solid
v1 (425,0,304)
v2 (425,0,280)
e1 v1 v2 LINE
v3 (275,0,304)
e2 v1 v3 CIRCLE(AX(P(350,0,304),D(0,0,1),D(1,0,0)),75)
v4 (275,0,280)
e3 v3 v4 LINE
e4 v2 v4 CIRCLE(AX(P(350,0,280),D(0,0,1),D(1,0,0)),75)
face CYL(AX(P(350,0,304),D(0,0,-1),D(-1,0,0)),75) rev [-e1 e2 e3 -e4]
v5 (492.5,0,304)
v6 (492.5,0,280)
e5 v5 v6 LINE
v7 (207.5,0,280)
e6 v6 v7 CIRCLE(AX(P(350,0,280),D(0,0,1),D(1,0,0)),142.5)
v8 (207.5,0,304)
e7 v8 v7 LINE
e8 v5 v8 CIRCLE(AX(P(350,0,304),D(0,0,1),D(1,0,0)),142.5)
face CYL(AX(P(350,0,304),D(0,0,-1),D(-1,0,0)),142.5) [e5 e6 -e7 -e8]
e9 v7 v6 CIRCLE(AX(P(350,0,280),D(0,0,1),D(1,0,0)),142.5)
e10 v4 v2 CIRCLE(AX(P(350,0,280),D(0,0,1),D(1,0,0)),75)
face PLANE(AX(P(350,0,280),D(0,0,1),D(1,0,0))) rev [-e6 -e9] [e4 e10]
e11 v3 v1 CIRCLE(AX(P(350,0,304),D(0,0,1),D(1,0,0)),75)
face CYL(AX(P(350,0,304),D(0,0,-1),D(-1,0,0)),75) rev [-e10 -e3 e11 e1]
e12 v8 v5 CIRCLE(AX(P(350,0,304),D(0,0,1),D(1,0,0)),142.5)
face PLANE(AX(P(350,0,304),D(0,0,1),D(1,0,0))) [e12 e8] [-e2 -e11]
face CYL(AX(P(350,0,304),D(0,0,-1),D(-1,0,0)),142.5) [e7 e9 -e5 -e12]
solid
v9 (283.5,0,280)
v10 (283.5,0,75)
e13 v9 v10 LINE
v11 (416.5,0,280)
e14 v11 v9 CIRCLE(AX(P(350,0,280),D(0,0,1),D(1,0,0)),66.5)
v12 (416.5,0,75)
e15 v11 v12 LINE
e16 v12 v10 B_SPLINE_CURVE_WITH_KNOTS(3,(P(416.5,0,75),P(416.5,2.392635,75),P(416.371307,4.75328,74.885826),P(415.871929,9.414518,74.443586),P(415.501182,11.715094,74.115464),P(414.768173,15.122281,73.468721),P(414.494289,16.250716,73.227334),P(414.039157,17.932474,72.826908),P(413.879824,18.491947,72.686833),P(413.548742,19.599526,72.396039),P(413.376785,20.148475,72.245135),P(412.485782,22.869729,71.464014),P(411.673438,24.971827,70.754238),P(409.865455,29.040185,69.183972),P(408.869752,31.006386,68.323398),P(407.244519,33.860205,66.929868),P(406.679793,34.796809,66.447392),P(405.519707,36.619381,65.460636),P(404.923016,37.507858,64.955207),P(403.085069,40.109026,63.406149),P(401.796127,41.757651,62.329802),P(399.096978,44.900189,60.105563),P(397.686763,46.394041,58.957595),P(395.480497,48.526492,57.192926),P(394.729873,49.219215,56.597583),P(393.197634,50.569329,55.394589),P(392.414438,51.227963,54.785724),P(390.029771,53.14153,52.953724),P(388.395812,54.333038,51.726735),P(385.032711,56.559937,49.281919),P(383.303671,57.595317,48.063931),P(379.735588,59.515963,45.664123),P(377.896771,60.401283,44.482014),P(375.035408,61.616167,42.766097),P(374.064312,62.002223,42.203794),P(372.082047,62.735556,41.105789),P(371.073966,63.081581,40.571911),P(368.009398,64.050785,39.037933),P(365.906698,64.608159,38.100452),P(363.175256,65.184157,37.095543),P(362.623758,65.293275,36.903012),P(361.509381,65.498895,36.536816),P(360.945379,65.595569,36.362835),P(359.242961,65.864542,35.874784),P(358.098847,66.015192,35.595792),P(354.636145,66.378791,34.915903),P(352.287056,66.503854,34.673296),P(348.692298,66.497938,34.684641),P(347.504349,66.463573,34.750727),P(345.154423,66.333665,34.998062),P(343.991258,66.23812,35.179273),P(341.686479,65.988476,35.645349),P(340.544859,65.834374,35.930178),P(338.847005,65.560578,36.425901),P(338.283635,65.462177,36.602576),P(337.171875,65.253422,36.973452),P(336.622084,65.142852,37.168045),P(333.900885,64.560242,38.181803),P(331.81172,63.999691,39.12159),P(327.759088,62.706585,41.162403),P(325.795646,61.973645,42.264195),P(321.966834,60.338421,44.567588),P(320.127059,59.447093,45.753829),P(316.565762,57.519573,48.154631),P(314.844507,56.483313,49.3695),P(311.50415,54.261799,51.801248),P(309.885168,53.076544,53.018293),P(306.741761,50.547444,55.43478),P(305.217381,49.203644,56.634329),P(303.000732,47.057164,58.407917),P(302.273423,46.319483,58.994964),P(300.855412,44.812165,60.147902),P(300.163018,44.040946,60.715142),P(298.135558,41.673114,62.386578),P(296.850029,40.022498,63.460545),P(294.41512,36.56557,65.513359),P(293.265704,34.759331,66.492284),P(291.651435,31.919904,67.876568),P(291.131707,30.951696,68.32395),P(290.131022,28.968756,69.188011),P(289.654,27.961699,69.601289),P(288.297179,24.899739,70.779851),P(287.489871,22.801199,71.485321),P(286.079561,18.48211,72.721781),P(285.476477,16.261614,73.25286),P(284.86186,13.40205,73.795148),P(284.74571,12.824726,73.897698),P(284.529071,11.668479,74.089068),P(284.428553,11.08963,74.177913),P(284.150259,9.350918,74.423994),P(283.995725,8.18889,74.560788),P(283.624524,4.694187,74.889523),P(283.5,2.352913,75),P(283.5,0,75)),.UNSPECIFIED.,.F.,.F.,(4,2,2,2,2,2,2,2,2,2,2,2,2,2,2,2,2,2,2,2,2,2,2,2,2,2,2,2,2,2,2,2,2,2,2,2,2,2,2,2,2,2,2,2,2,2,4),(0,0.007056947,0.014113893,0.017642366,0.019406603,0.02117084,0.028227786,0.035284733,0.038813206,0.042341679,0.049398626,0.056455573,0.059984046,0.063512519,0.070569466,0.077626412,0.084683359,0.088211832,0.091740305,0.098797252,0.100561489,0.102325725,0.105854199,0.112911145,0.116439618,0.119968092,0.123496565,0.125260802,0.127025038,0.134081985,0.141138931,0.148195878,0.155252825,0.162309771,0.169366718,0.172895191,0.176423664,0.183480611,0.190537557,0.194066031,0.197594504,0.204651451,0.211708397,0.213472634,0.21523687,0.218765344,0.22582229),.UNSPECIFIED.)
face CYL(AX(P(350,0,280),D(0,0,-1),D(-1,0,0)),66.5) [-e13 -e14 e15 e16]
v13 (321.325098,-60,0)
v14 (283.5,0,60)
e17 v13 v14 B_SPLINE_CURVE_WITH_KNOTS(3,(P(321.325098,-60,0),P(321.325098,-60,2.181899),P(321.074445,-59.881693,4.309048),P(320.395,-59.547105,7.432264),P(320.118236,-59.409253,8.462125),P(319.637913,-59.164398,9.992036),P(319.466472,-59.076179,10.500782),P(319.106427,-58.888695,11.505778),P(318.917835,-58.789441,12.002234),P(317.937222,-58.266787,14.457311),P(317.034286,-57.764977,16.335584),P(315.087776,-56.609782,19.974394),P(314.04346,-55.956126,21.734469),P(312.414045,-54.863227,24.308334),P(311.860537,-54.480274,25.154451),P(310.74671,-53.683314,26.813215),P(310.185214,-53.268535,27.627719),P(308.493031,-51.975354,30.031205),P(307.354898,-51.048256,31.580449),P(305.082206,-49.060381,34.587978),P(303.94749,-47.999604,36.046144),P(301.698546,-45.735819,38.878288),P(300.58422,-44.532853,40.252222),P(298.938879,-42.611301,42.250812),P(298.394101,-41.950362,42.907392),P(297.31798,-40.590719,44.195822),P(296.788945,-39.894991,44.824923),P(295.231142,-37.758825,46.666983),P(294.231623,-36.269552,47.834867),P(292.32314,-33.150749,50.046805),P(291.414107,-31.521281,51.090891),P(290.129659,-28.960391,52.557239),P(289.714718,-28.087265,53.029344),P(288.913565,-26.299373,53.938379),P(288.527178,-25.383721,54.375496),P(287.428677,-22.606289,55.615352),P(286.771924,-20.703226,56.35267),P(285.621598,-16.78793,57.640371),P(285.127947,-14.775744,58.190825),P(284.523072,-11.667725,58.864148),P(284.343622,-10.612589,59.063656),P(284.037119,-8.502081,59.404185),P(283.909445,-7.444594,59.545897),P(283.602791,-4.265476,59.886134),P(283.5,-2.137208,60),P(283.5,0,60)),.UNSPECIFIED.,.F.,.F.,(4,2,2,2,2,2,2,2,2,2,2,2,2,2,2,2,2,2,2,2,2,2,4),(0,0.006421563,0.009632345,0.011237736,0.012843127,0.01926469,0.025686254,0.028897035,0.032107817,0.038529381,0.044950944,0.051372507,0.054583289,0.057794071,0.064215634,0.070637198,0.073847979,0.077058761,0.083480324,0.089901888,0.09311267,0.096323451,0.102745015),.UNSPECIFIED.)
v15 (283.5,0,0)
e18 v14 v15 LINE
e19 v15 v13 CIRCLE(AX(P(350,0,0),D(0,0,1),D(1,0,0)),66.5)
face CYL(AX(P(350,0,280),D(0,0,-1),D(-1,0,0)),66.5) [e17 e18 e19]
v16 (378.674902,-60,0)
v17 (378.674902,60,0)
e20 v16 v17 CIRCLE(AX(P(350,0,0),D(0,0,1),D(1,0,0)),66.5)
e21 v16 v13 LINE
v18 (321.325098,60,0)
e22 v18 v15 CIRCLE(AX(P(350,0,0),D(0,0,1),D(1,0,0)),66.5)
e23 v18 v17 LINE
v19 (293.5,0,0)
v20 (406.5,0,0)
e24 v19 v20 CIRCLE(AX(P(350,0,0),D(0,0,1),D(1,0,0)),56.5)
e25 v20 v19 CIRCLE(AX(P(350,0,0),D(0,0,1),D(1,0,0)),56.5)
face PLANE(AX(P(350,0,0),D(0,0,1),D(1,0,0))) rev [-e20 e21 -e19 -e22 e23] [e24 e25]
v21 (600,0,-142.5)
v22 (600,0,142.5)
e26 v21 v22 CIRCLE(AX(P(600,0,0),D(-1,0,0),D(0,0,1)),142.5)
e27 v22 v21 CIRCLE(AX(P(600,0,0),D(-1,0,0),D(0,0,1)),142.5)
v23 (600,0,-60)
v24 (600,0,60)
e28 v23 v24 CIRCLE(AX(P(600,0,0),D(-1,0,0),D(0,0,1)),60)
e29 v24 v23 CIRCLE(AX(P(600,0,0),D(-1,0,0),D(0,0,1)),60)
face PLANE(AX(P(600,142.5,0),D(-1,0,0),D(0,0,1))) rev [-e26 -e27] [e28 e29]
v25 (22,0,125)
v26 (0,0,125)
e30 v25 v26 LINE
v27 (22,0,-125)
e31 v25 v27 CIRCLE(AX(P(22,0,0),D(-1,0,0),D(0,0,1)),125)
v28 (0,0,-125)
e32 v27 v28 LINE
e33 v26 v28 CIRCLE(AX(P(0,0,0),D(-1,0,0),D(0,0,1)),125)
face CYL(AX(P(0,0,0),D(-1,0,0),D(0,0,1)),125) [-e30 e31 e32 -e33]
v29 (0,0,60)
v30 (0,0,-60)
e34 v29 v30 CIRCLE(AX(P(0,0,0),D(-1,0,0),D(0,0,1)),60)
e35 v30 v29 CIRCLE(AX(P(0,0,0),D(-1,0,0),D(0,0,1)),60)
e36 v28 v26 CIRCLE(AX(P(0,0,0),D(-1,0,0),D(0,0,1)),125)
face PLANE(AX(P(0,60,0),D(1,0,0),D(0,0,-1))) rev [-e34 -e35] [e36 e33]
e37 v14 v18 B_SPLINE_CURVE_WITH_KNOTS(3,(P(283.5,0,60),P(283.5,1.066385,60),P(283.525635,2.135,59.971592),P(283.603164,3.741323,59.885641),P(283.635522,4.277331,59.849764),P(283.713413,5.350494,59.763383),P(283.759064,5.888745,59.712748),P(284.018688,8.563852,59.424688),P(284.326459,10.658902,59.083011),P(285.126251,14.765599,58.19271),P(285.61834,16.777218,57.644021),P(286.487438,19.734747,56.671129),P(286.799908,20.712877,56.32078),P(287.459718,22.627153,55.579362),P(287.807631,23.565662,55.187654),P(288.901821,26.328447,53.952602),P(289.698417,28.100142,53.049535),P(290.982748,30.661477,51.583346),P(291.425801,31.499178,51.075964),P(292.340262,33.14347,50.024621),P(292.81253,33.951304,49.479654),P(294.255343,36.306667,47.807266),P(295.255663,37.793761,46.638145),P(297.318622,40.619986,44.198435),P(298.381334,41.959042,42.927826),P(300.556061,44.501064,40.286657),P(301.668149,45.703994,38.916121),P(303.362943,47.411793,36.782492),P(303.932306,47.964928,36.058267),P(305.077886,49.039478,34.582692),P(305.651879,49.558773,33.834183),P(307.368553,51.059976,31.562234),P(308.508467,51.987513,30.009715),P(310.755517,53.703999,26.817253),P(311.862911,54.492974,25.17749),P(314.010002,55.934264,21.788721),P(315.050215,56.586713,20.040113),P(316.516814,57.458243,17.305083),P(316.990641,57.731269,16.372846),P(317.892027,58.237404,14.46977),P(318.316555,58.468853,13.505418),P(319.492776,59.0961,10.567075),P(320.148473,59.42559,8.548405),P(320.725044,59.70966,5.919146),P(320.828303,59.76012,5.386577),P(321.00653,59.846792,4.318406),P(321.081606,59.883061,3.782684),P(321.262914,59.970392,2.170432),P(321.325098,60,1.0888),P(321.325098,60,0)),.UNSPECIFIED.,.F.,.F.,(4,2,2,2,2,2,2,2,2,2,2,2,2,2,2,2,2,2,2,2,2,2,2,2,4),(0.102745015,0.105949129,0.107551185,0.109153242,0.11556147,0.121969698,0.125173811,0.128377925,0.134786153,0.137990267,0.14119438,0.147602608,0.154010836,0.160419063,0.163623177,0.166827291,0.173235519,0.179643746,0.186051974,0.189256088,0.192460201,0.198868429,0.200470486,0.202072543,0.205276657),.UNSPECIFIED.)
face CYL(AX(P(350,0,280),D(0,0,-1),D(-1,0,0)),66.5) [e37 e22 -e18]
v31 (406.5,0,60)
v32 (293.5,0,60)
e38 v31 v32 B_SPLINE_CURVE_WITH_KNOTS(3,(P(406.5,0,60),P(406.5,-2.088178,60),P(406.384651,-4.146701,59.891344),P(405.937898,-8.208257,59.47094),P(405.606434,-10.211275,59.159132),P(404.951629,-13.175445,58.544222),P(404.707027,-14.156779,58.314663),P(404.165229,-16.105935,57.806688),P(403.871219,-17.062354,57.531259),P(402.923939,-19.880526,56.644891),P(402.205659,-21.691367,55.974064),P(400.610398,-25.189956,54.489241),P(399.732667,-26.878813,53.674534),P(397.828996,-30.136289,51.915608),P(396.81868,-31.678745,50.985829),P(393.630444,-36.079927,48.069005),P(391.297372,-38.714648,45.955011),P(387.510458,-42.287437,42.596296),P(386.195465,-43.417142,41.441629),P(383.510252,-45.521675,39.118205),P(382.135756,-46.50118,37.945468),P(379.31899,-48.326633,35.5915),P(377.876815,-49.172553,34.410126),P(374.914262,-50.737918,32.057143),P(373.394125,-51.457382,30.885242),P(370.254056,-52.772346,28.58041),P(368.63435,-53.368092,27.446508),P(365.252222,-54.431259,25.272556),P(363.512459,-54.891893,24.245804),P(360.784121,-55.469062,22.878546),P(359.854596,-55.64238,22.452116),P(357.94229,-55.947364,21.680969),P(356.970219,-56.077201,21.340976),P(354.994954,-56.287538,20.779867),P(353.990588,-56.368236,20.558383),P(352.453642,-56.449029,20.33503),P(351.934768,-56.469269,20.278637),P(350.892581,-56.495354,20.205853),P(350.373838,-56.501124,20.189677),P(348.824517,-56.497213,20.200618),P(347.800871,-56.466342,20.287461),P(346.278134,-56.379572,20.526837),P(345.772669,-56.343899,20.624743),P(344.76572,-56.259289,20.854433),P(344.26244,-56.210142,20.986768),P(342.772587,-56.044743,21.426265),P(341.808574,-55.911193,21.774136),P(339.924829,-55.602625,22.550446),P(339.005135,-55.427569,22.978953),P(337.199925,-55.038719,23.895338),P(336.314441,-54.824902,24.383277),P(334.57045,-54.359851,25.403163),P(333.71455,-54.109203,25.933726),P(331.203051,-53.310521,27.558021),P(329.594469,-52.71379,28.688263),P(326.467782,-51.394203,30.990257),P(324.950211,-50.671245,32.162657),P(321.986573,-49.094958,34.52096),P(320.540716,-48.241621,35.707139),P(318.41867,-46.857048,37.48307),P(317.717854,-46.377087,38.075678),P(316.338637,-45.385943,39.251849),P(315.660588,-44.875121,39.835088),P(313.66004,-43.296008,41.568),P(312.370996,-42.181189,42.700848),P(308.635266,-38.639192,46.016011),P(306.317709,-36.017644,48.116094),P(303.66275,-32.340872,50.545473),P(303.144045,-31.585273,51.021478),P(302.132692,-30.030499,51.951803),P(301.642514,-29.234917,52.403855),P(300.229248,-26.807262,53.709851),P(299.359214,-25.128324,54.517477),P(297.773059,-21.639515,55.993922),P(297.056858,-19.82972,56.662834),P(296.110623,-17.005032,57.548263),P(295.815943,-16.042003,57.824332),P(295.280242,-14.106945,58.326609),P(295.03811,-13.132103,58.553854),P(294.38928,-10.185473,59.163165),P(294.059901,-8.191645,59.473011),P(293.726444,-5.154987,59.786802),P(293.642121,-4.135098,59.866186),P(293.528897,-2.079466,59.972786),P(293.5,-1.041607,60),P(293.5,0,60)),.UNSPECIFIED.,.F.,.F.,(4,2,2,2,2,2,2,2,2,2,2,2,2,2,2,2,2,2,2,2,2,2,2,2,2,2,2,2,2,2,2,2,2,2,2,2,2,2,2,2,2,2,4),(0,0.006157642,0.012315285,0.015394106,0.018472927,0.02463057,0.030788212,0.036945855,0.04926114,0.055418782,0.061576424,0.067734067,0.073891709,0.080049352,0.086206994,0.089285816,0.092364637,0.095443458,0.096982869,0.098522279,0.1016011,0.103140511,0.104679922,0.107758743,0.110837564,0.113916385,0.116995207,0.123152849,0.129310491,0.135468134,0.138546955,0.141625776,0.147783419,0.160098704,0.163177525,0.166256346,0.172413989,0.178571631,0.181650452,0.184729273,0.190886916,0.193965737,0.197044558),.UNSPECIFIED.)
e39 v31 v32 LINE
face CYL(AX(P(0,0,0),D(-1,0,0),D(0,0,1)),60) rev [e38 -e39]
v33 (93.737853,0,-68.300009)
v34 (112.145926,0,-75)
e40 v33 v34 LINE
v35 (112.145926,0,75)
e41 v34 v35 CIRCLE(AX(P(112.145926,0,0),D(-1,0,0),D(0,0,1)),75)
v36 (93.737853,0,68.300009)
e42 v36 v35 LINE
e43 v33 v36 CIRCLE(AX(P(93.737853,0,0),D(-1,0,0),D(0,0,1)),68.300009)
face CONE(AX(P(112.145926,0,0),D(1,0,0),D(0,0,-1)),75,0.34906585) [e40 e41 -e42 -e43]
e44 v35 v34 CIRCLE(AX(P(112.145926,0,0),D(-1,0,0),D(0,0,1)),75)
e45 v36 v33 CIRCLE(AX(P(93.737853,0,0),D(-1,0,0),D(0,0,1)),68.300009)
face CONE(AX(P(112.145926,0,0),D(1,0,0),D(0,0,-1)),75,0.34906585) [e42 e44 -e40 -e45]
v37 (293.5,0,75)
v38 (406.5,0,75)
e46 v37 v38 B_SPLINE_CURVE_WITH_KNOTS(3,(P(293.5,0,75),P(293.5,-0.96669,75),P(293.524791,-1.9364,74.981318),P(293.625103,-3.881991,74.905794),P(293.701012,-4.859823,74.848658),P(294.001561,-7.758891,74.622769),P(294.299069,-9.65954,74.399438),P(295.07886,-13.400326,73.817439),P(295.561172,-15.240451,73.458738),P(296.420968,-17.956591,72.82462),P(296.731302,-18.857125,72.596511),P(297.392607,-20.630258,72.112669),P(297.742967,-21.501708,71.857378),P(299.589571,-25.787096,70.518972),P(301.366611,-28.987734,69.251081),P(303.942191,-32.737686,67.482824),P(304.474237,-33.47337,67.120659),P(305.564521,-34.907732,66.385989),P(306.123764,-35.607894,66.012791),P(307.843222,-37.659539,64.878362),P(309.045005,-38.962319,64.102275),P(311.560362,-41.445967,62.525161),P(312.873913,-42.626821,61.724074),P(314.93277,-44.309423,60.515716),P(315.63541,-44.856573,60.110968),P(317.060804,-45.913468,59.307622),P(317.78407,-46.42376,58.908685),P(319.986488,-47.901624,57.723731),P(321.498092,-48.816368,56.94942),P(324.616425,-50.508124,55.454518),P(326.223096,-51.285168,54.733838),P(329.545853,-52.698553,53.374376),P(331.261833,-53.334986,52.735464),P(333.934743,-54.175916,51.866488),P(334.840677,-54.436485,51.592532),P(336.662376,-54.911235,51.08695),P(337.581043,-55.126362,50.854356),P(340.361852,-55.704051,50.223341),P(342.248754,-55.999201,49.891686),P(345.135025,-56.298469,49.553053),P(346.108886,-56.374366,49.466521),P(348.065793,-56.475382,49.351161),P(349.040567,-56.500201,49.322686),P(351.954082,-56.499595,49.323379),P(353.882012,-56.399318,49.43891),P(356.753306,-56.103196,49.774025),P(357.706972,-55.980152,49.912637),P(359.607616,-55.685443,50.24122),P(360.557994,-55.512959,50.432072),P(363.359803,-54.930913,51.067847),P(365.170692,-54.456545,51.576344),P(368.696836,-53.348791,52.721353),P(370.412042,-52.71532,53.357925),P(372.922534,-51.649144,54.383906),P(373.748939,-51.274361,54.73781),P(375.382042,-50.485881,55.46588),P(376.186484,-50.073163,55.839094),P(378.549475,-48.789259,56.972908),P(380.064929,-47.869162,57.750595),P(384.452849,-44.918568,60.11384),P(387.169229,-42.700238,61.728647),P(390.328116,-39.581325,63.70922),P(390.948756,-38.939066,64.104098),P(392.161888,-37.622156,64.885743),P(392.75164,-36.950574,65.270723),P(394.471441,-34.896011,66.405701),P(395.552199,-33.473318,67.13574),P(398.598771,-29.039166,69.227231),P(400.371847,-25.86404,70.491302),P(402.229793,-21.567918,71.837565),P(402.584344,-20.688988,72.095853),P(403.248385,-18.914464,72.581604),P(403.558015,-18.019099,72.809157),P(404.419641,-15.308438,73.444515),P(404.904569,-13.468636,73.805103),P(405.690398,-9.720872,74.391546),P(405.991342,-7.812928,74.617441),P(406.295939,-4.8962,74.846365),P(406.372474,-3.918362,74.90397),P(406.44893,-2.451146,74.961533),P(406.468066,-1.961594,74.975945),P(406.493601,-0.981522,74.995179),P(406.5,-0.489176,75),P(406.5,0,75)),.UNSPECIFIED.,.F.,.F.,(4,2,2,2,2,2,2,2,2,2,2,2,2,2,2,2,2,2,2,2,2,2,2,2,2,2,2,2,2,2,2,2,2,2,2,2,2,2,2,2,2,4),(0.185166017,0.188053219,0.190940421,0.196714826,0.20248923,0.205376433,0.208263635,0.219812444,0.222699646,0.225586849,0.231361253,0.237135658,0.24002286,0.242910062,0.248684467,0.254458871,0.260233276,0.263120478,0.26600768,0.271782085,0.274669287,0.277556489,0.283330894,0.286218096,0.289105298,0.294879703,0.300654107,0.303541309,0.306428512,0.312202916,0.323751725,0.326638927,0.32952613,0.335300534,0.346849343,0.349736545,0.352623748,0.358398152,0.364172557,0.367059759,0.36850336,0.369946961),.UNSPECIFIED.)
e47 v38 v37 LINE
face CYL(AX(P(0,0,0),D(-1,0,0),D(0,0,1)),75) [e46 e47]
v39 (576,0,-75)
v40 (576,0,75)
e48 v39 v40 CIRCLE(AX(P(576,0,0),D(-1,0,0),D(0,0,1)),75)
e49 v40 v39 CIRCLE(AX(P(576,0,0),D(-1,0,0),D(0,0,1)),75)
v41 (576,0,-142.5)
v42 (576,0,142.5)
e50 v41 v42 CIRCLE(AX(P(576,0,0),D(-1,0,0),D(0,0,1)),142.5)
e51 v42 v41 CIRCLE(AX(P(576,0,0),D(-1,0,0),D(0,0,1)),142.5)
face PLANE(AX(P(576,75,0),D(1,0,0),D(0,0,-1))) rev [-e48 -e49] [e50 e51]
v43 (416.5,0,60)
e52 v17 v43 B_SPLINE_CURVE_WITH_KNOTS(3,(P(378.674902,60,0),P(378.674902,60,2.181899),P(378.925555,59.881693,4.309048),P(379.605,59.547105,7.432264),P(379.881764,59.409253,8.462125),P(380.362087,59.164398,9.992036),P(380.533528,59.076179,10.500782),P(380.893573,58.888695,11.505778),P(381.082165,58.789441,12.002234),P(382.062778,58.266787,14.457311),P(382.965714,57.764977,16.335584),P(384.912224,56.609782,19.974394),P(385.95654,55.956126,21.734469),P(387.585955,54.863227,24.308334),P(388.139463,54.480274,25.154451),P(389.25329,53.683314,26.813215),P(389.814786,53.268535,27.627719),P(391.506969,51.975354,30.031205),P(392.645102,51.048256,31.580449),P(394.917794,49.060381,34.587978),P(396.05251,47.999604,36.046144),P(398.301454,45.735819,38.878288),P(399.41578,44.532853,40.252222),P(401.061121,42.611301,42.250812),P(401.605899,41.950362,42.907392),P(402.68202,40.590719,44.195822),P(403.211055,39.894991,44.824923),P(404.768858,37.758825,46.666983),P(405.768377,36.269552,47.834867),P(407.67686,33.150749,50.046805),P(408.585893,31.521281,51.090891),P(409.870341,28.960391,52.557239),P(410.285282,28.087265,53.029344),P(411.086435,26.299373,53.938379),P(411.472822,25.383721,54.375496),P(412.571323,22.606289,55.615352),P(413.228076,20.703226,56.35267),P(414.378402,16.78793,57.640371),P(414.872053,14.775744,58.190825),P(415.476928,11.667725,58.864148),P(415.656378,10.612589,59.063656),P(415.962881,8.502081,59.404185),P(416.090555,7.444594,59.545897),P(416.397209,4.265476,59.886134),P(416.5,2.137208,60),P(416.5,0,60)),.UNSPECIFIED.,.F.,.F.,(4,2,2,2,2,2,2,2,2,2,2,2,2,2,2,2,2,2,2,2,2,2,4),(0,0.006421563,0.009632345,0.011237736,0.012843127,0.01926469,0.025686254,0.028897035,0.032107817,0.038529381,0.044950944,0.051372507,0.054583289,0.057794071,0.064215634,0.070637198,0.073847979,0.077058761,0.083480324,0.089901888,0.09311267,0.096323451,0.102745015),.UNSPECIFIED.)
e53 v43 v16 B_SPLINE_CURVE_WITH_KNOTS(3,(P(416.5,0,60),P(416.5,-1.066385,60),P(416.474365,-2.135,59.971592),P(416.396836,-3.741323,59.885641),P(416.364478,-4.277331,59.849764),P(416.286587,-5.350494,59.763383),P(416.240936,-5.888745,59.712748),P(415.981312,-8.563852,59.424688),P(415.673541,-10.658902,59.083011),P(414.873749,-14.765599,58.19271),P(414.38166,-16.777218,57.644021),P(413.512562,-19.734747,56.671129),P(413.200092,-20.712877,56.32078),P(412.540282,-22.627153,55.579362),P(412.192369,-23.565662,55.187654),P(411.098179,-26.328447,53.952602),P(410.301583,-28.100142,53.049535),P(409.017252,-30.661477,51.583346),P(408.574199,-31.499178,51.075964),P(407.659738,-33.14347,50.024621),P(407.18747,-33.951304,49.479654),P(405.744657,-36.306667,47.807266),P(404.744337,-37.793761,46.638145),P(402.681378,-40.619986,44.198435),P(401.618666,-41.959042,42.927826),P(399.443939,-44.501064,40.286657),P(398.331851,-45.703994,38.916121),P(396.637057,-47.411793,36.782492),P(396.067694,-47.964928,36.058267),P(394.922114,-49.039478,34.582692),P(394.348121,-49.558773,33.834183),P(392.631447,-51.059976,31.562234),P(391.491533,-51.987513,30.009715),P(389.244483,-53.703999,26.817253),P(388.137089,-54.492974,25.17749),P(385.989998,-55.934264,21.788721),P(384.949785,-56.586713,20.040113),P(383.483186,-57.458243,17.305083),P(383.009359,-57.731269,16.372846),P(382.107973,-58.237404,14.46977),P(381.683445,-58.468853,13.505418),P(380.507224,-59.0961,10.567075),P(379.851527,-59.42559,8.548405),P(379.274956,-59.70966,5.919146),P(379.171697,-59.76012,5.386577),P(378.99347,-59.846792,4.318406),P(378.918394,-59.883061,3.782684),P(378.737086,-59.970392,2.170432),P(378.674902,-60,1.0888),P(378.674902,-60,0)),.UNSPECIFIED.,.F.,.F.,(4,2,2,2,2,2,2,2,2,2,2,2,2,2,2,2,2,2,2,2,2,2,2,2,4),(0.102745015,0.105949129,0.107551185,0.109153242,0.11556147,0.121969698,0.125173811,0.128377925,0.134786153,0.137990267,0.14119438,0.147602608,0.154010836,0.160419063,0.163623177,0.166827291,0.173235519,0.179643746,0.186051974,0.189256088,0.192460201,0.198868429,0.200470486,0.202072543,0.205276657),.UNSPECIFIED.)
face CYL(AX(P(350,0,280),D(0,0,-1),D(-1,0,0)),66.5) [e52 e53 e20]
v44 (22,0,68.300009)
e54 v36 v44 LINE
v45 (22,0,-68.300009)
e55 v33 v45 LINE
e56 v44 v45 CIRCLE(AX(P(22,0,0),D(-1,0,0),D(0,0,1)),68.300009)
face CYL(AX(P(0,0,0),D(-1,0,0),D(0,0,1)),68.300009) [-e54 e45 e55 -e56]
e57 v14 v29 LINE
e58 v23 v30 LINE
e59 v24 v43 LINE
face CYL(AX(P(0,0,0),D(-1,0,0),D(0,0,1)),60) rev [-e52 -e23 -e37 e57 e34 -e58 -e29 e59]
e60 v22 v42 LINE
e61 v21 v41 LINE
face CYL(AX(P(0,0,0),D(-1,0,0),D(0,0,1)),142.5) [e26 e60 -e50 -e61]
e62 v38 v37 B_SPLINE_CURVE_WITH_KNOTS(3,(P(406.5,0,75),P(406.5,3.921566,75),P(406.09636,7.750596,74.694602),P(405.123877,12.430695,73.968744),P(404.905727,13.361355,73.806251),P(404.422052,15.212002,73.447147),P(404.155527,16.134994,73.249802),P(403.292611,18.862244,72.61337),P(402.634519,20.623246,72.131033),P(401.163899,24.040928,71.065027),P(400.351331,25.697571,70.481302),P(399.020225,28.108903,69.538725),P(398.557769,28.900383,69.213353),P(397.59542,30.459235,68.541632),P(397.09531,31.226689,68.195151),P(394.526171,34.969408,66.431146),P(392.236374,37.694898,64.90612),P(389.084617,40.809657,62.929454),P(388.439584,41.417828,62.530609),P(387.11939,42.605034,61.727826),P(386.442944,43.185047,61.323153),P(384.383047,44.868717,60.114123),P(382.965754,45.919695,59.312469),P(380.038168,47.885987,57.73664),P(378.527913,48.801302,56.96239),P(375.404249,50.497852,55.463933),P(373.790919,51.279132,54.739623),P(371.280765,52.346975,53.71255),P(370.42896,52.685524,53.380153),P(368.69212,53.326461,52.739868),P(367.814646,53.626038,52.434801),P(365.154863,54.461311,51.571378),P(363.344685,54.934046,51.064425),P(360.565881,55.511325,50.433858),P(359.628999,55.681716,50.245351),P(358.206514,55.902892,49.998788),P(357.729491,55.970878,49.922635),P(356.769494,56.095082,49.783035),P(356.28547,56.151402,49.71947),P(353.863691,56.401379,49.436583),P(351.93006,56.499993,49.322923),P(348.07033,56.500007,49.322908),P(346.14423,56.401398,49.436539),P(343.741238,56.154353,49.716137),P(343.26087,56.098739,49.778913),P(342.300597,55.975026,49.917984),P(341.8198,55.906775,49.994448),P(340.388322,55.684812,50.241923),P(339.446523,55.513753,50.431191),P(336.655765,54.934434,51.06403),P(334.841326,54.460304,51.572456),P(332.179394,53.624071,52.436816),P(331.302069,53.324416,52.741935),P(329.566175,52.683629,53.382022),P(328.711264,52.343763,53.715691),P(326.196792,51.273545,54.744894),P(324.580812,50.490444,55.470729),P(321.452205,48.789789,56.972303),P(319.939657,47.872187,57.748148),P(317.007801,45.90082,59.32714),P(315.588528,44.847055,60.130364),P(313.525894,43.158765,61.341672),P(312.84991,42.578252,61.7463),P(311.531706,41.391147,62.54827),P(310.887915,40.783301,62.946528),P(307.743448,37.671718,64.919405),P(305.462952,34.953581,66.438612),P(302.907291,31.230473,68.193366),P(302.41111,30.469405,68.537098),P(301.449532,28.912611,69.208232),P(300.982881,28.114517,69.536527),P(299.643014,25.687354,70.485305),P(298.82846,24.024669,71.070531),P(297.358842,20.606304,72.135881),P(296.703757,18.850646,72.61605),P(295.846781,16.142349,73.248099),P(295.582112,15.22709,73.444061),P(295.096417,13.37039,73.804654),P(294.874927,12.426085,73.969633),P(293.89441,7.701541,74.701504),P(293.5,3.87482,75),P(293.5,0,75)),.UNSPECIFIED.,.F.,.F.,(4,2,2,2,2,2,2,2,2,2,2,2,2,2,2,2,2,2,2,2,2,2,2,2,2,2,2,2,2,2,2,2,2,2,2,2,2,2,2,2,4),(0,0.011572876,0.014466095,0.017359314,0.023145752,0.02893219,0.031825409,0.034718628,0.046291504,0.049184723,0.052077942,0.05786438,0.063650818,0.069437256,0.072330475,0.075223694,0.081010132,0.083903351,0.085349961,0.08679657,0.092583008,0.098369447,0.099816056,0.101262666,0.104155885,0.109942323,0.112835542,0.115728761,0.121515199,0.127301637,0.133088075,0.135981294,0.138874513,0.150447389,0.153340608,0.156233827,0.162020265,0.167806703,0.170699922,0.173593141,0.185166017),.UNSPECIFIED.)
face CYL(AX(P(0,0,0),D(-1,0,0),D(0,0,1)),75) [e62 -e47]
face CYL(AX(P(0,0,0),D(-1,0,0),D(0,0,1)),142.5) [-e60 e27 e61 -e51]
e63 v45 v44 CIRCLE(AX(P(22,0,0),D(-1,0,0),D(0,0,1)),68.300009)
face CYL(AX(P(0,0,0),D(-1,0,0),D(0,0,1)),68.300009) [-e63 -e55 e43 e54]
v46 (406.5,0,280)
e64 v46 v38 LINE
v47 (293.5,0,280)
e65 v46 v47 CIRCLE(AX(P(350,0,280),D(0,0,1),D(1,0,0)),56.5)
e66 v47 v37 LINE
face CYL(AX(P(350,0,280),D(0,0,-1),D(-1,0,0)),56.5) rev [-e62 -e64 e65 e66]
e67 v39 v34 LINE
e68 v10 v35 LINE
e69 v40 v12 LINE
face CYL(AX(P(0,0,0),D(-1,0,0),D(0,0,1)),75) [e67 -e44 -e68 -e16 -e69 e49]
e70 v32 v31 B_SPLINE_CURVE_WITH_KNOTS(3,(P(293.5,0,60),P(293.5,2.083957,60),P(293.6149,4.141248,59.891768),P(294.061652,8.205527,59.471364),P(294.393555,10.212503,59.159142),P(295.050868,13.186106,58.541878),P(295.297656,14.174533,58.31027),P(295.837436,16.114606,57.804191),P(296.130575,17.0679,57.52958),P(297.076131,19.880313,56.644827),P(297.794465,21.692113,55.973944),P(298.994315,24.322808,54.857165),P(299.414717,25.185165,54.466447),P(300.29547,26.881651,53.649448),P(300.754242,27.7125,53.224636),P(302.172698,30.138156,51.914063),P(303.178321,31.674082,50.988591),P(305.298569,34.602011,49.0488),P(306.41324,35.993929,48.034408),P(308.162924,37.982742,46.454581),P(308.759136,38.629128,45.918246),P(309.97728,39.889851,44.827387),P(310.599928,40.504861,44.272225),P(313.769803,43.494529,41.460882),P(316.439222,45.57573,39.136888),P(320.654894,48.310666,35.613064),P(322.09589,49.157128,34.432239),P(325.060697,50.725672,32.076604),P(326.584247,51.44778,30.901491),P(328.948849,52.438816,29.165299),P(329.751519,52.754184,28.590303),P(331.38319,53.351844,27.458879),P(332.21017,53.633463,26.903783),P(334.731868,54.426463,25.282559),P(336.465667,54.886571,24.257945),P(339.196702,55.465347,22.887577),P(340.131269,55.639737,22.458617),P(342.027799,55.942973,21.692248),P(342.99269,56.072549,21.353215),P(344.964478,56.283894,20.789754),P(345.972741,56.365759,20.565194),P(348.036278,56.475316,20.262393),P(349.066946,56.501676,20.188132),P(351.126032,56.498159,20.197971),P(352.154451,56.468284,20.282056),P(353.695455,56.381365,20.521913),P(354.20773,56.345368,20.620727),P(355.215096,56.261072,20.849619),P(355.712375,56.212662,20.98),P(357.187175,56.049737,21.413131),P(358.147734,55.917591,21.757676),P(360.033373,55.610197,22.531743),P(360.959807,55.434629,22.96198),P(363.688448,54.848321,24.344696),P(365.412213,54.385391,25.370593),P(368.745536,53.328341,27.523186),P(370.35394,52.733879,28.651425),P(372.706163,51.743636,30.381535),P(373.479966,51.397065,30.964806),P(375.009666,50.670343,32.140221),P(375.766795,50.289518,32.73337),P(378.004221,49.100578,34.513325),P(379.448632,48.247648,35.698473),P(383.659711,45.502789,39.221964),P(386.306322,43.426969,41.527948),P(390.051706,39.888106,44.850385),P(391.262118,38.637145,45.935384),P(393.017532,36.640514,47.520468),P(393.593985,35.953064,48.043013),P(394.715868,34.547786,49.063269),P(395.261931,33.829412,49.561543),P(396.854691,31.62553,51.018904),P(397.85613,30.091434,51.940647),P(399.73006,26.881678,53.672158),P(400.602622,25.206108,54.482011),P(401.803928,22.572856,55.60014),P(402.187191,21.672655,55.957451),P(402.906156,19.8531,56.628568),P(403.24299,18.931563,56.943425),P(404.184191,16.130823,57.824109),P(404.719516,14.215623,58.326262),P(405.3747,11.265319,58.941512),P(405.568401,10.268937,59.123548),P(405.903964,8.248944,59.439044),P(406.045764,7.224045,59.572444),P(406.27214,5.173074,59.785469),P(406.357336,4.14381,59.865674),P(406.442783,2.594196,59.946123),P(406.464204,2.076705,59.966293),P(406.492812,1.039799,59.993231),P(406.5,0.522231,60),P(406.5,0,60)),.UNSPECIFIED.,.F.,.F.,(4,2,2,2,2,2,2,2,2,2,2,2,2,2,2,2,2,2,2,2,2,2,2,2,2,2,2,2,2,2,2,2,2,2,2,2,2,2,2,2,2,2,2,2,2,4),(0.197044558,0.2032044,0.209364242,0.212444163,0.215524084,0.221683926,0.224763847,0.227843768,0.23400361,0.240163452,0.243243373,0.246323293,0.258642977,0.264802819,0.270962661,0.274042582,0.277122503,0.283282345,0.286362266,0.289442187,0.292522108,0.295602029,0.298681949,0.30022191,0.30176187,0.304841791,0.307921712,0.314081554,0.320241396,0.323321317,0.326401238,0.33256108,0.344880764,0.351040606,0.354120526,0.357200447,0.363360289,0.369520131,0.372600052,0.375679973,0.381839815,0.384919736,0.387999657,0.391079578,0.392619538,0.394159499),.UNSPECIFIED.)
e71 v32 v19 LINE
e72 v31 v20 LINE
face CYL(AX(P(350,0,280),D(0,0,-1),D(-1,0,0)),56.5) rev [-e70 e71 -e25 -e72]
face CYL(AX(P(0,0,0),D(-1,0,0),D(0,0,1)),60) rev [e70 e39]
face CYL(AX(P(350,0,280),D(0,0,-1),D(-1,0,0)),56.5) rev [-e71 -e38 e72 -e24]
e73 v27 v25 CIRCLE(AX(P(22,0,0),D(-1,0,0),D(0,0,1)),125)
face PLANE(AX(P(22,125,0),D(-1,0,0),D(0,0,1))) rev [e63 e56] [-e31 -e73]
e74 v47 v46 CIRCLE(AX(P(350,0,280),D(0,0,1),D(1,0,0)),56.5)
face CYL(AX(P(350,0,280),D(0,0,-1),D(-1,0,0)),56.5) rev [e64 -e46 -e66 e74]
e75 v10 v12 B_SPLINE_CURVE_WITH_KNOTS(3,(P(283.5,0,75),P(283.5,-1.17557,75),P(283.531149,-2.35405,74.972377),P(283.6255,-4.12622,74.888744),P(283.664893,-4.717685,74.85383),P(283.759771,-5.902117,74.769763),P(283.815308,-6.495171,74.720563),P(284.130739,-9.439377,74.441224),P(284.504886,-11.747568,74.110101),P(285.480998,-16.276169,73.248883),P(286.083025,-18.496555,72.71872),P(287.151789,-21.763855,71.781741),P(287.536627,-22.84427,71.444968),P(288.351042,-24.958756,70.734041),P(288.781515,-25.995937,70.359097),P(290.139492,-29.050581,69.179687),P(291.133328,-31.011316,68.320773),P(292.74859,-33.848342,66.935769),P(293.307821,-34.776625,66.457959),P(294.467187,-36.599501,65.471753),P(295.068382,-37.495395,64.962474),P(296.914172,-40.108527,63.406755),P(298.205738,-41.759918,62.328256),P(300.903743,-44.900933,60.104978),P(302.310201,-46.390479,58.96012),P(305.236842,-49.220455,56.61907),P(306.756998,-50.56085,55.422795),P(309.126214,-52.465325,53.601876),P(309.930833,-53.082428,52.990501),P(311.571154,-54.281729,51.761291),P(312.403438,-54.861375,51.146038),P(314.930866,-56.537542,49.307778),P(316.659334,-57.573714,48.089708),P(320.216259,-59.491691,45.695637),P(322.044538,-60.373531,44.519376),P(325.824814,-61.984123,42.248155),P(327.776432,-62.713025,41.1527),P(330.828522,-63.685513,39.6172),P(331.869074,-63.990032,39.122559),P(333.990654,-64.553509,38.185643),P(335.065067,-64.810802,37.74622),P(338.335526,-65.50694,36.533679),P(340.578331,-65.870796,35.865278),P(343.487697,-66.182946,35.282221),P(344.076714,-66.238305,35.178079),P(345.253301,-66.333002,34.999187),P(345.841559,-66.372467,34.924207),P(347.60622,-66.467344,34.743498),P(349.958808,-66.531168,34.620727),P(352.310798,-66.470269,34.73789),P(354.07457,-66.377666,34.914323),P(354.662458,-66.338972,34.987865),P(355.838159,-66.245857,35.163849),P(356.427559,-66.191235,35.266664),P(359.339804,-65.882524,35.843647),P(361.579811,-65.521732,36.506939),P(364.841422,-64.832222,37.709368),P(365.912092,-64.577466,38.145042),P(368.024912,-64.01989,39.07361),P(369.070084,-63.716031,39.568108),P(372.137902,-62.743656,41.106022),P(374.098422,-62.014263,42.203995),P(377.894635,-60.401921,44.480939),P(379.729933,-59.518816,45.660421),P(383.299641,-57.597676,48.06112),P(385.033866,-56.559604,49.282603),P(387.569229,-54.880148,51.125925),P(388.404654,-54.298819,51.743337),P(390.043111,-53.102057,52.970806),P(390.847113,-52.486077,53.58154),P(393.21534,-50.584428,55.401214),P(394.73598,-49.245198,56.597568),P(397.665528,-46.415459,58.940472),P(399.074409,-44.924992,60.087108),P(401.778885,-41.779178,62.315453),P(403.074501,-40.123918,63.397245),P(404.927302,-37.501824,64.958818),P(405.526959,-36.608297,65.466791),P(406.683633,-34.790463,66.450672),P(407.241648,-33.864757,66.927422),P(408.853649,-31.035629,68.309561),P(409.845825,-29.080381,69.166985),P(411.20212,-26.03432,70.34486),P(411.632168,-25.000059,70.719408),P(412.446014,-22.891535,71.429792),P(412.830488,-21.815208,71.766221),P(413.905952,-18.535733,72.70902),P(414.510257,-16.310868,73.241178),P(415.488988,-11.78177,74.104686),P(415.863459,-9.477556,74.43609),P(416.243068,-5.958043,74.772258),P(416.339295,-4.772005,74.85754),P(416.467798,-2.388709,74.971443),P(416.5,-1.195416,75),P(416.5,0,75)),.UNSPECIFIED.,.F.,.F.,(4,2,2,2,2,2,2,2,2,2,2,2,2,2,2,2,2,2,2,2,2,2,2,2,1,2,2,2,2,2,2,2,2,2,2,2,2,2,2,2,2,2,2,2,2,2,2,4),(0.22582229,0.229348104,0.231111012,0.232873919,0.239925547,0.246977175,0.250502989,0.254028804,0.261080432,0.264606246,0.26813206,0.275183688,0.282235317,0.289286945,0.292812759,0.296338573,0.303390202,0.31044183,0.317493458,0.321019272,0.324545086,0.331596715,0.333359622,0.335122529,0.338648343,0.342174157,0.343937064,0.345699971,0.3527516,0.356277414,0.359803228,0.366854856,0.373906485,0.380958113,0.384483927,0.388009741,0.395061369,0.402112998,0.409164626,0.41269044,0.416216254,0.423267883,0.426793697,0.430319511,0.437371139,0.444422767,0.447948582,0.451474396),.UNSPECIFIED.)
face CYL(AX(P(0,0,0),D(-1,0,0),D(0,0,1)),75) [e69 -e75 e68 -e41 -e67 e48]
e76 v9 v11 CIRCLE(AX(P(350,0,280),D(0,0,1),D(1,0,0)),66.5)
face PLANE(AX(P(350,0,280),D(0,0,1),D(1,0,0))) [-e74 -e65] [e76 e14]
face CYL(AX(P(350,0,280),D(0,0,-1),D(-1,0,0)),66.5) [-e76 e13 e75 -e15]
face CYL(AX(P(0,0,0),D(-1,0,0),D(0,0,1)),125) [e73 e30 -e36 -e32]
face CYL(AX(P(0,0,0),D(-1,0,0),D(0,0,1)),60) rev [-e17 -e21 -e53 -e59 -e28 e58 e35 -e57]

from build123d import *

# Parameters (mm, degrees)
SKETCH2_R           = 66.5
SKETCH2_R_2         = 56.5
BOSS_EXTRUDE1_DEPTH = 280
SKETCH3_R           = 142.5
SKETCH3_R_2         = 75
BOSS_EXTRUDE2_DEPTH = 24


with BuildPart() as part:
    # Sketch1 → Revolve1 (revolve)
    with BuildSketch(Plane.XY, mode=Mode.PRIVATE) as revolve1_sk:
        Polygon((0, 60), (0, 125), (22, 125), (22, 68.30000917), (93.737852553, 68.30000917), (112.145926068, 75), (576, 75), (576, 142.5), (600, 142.5), (600, 60), align=None)
    revolve(revolve1_sk.sketch.rotate(Axis((0, 0, 0), (1, 0, 0)), 90), axis=Axis((0, 0, 0), (1, 0, 0)))

    # Sketch2 → Boss-Extrude1 (add)
    with BuildSketch(Plane.XY):
        with Locations((350, 0)):
            Circle(SKETCH2_R)
        with Locations((350, 0)):
            Circle(SKETCH2_R_2, mode=Mode.SUBTRACT)
    extrude(amount=BOSS_EXTRUDE1_DEPTH)


with BuildPart() as body_2:
    # Sketch3 → Boss-Extrude2 (new body)
    with BuildSketch(Plane.XY.offset(280)):
        with Locations((350, 0)):
            Circle(SKETCH3_R)
        with Locations((350, 0)):
            Circle(SKETCH3_R_2, mode=Mode.SUBTRACT)
    extrude(amount=BOSS_EXTRUDE2_DEPTH)


solid = Compound([part.part, body_2.part])
